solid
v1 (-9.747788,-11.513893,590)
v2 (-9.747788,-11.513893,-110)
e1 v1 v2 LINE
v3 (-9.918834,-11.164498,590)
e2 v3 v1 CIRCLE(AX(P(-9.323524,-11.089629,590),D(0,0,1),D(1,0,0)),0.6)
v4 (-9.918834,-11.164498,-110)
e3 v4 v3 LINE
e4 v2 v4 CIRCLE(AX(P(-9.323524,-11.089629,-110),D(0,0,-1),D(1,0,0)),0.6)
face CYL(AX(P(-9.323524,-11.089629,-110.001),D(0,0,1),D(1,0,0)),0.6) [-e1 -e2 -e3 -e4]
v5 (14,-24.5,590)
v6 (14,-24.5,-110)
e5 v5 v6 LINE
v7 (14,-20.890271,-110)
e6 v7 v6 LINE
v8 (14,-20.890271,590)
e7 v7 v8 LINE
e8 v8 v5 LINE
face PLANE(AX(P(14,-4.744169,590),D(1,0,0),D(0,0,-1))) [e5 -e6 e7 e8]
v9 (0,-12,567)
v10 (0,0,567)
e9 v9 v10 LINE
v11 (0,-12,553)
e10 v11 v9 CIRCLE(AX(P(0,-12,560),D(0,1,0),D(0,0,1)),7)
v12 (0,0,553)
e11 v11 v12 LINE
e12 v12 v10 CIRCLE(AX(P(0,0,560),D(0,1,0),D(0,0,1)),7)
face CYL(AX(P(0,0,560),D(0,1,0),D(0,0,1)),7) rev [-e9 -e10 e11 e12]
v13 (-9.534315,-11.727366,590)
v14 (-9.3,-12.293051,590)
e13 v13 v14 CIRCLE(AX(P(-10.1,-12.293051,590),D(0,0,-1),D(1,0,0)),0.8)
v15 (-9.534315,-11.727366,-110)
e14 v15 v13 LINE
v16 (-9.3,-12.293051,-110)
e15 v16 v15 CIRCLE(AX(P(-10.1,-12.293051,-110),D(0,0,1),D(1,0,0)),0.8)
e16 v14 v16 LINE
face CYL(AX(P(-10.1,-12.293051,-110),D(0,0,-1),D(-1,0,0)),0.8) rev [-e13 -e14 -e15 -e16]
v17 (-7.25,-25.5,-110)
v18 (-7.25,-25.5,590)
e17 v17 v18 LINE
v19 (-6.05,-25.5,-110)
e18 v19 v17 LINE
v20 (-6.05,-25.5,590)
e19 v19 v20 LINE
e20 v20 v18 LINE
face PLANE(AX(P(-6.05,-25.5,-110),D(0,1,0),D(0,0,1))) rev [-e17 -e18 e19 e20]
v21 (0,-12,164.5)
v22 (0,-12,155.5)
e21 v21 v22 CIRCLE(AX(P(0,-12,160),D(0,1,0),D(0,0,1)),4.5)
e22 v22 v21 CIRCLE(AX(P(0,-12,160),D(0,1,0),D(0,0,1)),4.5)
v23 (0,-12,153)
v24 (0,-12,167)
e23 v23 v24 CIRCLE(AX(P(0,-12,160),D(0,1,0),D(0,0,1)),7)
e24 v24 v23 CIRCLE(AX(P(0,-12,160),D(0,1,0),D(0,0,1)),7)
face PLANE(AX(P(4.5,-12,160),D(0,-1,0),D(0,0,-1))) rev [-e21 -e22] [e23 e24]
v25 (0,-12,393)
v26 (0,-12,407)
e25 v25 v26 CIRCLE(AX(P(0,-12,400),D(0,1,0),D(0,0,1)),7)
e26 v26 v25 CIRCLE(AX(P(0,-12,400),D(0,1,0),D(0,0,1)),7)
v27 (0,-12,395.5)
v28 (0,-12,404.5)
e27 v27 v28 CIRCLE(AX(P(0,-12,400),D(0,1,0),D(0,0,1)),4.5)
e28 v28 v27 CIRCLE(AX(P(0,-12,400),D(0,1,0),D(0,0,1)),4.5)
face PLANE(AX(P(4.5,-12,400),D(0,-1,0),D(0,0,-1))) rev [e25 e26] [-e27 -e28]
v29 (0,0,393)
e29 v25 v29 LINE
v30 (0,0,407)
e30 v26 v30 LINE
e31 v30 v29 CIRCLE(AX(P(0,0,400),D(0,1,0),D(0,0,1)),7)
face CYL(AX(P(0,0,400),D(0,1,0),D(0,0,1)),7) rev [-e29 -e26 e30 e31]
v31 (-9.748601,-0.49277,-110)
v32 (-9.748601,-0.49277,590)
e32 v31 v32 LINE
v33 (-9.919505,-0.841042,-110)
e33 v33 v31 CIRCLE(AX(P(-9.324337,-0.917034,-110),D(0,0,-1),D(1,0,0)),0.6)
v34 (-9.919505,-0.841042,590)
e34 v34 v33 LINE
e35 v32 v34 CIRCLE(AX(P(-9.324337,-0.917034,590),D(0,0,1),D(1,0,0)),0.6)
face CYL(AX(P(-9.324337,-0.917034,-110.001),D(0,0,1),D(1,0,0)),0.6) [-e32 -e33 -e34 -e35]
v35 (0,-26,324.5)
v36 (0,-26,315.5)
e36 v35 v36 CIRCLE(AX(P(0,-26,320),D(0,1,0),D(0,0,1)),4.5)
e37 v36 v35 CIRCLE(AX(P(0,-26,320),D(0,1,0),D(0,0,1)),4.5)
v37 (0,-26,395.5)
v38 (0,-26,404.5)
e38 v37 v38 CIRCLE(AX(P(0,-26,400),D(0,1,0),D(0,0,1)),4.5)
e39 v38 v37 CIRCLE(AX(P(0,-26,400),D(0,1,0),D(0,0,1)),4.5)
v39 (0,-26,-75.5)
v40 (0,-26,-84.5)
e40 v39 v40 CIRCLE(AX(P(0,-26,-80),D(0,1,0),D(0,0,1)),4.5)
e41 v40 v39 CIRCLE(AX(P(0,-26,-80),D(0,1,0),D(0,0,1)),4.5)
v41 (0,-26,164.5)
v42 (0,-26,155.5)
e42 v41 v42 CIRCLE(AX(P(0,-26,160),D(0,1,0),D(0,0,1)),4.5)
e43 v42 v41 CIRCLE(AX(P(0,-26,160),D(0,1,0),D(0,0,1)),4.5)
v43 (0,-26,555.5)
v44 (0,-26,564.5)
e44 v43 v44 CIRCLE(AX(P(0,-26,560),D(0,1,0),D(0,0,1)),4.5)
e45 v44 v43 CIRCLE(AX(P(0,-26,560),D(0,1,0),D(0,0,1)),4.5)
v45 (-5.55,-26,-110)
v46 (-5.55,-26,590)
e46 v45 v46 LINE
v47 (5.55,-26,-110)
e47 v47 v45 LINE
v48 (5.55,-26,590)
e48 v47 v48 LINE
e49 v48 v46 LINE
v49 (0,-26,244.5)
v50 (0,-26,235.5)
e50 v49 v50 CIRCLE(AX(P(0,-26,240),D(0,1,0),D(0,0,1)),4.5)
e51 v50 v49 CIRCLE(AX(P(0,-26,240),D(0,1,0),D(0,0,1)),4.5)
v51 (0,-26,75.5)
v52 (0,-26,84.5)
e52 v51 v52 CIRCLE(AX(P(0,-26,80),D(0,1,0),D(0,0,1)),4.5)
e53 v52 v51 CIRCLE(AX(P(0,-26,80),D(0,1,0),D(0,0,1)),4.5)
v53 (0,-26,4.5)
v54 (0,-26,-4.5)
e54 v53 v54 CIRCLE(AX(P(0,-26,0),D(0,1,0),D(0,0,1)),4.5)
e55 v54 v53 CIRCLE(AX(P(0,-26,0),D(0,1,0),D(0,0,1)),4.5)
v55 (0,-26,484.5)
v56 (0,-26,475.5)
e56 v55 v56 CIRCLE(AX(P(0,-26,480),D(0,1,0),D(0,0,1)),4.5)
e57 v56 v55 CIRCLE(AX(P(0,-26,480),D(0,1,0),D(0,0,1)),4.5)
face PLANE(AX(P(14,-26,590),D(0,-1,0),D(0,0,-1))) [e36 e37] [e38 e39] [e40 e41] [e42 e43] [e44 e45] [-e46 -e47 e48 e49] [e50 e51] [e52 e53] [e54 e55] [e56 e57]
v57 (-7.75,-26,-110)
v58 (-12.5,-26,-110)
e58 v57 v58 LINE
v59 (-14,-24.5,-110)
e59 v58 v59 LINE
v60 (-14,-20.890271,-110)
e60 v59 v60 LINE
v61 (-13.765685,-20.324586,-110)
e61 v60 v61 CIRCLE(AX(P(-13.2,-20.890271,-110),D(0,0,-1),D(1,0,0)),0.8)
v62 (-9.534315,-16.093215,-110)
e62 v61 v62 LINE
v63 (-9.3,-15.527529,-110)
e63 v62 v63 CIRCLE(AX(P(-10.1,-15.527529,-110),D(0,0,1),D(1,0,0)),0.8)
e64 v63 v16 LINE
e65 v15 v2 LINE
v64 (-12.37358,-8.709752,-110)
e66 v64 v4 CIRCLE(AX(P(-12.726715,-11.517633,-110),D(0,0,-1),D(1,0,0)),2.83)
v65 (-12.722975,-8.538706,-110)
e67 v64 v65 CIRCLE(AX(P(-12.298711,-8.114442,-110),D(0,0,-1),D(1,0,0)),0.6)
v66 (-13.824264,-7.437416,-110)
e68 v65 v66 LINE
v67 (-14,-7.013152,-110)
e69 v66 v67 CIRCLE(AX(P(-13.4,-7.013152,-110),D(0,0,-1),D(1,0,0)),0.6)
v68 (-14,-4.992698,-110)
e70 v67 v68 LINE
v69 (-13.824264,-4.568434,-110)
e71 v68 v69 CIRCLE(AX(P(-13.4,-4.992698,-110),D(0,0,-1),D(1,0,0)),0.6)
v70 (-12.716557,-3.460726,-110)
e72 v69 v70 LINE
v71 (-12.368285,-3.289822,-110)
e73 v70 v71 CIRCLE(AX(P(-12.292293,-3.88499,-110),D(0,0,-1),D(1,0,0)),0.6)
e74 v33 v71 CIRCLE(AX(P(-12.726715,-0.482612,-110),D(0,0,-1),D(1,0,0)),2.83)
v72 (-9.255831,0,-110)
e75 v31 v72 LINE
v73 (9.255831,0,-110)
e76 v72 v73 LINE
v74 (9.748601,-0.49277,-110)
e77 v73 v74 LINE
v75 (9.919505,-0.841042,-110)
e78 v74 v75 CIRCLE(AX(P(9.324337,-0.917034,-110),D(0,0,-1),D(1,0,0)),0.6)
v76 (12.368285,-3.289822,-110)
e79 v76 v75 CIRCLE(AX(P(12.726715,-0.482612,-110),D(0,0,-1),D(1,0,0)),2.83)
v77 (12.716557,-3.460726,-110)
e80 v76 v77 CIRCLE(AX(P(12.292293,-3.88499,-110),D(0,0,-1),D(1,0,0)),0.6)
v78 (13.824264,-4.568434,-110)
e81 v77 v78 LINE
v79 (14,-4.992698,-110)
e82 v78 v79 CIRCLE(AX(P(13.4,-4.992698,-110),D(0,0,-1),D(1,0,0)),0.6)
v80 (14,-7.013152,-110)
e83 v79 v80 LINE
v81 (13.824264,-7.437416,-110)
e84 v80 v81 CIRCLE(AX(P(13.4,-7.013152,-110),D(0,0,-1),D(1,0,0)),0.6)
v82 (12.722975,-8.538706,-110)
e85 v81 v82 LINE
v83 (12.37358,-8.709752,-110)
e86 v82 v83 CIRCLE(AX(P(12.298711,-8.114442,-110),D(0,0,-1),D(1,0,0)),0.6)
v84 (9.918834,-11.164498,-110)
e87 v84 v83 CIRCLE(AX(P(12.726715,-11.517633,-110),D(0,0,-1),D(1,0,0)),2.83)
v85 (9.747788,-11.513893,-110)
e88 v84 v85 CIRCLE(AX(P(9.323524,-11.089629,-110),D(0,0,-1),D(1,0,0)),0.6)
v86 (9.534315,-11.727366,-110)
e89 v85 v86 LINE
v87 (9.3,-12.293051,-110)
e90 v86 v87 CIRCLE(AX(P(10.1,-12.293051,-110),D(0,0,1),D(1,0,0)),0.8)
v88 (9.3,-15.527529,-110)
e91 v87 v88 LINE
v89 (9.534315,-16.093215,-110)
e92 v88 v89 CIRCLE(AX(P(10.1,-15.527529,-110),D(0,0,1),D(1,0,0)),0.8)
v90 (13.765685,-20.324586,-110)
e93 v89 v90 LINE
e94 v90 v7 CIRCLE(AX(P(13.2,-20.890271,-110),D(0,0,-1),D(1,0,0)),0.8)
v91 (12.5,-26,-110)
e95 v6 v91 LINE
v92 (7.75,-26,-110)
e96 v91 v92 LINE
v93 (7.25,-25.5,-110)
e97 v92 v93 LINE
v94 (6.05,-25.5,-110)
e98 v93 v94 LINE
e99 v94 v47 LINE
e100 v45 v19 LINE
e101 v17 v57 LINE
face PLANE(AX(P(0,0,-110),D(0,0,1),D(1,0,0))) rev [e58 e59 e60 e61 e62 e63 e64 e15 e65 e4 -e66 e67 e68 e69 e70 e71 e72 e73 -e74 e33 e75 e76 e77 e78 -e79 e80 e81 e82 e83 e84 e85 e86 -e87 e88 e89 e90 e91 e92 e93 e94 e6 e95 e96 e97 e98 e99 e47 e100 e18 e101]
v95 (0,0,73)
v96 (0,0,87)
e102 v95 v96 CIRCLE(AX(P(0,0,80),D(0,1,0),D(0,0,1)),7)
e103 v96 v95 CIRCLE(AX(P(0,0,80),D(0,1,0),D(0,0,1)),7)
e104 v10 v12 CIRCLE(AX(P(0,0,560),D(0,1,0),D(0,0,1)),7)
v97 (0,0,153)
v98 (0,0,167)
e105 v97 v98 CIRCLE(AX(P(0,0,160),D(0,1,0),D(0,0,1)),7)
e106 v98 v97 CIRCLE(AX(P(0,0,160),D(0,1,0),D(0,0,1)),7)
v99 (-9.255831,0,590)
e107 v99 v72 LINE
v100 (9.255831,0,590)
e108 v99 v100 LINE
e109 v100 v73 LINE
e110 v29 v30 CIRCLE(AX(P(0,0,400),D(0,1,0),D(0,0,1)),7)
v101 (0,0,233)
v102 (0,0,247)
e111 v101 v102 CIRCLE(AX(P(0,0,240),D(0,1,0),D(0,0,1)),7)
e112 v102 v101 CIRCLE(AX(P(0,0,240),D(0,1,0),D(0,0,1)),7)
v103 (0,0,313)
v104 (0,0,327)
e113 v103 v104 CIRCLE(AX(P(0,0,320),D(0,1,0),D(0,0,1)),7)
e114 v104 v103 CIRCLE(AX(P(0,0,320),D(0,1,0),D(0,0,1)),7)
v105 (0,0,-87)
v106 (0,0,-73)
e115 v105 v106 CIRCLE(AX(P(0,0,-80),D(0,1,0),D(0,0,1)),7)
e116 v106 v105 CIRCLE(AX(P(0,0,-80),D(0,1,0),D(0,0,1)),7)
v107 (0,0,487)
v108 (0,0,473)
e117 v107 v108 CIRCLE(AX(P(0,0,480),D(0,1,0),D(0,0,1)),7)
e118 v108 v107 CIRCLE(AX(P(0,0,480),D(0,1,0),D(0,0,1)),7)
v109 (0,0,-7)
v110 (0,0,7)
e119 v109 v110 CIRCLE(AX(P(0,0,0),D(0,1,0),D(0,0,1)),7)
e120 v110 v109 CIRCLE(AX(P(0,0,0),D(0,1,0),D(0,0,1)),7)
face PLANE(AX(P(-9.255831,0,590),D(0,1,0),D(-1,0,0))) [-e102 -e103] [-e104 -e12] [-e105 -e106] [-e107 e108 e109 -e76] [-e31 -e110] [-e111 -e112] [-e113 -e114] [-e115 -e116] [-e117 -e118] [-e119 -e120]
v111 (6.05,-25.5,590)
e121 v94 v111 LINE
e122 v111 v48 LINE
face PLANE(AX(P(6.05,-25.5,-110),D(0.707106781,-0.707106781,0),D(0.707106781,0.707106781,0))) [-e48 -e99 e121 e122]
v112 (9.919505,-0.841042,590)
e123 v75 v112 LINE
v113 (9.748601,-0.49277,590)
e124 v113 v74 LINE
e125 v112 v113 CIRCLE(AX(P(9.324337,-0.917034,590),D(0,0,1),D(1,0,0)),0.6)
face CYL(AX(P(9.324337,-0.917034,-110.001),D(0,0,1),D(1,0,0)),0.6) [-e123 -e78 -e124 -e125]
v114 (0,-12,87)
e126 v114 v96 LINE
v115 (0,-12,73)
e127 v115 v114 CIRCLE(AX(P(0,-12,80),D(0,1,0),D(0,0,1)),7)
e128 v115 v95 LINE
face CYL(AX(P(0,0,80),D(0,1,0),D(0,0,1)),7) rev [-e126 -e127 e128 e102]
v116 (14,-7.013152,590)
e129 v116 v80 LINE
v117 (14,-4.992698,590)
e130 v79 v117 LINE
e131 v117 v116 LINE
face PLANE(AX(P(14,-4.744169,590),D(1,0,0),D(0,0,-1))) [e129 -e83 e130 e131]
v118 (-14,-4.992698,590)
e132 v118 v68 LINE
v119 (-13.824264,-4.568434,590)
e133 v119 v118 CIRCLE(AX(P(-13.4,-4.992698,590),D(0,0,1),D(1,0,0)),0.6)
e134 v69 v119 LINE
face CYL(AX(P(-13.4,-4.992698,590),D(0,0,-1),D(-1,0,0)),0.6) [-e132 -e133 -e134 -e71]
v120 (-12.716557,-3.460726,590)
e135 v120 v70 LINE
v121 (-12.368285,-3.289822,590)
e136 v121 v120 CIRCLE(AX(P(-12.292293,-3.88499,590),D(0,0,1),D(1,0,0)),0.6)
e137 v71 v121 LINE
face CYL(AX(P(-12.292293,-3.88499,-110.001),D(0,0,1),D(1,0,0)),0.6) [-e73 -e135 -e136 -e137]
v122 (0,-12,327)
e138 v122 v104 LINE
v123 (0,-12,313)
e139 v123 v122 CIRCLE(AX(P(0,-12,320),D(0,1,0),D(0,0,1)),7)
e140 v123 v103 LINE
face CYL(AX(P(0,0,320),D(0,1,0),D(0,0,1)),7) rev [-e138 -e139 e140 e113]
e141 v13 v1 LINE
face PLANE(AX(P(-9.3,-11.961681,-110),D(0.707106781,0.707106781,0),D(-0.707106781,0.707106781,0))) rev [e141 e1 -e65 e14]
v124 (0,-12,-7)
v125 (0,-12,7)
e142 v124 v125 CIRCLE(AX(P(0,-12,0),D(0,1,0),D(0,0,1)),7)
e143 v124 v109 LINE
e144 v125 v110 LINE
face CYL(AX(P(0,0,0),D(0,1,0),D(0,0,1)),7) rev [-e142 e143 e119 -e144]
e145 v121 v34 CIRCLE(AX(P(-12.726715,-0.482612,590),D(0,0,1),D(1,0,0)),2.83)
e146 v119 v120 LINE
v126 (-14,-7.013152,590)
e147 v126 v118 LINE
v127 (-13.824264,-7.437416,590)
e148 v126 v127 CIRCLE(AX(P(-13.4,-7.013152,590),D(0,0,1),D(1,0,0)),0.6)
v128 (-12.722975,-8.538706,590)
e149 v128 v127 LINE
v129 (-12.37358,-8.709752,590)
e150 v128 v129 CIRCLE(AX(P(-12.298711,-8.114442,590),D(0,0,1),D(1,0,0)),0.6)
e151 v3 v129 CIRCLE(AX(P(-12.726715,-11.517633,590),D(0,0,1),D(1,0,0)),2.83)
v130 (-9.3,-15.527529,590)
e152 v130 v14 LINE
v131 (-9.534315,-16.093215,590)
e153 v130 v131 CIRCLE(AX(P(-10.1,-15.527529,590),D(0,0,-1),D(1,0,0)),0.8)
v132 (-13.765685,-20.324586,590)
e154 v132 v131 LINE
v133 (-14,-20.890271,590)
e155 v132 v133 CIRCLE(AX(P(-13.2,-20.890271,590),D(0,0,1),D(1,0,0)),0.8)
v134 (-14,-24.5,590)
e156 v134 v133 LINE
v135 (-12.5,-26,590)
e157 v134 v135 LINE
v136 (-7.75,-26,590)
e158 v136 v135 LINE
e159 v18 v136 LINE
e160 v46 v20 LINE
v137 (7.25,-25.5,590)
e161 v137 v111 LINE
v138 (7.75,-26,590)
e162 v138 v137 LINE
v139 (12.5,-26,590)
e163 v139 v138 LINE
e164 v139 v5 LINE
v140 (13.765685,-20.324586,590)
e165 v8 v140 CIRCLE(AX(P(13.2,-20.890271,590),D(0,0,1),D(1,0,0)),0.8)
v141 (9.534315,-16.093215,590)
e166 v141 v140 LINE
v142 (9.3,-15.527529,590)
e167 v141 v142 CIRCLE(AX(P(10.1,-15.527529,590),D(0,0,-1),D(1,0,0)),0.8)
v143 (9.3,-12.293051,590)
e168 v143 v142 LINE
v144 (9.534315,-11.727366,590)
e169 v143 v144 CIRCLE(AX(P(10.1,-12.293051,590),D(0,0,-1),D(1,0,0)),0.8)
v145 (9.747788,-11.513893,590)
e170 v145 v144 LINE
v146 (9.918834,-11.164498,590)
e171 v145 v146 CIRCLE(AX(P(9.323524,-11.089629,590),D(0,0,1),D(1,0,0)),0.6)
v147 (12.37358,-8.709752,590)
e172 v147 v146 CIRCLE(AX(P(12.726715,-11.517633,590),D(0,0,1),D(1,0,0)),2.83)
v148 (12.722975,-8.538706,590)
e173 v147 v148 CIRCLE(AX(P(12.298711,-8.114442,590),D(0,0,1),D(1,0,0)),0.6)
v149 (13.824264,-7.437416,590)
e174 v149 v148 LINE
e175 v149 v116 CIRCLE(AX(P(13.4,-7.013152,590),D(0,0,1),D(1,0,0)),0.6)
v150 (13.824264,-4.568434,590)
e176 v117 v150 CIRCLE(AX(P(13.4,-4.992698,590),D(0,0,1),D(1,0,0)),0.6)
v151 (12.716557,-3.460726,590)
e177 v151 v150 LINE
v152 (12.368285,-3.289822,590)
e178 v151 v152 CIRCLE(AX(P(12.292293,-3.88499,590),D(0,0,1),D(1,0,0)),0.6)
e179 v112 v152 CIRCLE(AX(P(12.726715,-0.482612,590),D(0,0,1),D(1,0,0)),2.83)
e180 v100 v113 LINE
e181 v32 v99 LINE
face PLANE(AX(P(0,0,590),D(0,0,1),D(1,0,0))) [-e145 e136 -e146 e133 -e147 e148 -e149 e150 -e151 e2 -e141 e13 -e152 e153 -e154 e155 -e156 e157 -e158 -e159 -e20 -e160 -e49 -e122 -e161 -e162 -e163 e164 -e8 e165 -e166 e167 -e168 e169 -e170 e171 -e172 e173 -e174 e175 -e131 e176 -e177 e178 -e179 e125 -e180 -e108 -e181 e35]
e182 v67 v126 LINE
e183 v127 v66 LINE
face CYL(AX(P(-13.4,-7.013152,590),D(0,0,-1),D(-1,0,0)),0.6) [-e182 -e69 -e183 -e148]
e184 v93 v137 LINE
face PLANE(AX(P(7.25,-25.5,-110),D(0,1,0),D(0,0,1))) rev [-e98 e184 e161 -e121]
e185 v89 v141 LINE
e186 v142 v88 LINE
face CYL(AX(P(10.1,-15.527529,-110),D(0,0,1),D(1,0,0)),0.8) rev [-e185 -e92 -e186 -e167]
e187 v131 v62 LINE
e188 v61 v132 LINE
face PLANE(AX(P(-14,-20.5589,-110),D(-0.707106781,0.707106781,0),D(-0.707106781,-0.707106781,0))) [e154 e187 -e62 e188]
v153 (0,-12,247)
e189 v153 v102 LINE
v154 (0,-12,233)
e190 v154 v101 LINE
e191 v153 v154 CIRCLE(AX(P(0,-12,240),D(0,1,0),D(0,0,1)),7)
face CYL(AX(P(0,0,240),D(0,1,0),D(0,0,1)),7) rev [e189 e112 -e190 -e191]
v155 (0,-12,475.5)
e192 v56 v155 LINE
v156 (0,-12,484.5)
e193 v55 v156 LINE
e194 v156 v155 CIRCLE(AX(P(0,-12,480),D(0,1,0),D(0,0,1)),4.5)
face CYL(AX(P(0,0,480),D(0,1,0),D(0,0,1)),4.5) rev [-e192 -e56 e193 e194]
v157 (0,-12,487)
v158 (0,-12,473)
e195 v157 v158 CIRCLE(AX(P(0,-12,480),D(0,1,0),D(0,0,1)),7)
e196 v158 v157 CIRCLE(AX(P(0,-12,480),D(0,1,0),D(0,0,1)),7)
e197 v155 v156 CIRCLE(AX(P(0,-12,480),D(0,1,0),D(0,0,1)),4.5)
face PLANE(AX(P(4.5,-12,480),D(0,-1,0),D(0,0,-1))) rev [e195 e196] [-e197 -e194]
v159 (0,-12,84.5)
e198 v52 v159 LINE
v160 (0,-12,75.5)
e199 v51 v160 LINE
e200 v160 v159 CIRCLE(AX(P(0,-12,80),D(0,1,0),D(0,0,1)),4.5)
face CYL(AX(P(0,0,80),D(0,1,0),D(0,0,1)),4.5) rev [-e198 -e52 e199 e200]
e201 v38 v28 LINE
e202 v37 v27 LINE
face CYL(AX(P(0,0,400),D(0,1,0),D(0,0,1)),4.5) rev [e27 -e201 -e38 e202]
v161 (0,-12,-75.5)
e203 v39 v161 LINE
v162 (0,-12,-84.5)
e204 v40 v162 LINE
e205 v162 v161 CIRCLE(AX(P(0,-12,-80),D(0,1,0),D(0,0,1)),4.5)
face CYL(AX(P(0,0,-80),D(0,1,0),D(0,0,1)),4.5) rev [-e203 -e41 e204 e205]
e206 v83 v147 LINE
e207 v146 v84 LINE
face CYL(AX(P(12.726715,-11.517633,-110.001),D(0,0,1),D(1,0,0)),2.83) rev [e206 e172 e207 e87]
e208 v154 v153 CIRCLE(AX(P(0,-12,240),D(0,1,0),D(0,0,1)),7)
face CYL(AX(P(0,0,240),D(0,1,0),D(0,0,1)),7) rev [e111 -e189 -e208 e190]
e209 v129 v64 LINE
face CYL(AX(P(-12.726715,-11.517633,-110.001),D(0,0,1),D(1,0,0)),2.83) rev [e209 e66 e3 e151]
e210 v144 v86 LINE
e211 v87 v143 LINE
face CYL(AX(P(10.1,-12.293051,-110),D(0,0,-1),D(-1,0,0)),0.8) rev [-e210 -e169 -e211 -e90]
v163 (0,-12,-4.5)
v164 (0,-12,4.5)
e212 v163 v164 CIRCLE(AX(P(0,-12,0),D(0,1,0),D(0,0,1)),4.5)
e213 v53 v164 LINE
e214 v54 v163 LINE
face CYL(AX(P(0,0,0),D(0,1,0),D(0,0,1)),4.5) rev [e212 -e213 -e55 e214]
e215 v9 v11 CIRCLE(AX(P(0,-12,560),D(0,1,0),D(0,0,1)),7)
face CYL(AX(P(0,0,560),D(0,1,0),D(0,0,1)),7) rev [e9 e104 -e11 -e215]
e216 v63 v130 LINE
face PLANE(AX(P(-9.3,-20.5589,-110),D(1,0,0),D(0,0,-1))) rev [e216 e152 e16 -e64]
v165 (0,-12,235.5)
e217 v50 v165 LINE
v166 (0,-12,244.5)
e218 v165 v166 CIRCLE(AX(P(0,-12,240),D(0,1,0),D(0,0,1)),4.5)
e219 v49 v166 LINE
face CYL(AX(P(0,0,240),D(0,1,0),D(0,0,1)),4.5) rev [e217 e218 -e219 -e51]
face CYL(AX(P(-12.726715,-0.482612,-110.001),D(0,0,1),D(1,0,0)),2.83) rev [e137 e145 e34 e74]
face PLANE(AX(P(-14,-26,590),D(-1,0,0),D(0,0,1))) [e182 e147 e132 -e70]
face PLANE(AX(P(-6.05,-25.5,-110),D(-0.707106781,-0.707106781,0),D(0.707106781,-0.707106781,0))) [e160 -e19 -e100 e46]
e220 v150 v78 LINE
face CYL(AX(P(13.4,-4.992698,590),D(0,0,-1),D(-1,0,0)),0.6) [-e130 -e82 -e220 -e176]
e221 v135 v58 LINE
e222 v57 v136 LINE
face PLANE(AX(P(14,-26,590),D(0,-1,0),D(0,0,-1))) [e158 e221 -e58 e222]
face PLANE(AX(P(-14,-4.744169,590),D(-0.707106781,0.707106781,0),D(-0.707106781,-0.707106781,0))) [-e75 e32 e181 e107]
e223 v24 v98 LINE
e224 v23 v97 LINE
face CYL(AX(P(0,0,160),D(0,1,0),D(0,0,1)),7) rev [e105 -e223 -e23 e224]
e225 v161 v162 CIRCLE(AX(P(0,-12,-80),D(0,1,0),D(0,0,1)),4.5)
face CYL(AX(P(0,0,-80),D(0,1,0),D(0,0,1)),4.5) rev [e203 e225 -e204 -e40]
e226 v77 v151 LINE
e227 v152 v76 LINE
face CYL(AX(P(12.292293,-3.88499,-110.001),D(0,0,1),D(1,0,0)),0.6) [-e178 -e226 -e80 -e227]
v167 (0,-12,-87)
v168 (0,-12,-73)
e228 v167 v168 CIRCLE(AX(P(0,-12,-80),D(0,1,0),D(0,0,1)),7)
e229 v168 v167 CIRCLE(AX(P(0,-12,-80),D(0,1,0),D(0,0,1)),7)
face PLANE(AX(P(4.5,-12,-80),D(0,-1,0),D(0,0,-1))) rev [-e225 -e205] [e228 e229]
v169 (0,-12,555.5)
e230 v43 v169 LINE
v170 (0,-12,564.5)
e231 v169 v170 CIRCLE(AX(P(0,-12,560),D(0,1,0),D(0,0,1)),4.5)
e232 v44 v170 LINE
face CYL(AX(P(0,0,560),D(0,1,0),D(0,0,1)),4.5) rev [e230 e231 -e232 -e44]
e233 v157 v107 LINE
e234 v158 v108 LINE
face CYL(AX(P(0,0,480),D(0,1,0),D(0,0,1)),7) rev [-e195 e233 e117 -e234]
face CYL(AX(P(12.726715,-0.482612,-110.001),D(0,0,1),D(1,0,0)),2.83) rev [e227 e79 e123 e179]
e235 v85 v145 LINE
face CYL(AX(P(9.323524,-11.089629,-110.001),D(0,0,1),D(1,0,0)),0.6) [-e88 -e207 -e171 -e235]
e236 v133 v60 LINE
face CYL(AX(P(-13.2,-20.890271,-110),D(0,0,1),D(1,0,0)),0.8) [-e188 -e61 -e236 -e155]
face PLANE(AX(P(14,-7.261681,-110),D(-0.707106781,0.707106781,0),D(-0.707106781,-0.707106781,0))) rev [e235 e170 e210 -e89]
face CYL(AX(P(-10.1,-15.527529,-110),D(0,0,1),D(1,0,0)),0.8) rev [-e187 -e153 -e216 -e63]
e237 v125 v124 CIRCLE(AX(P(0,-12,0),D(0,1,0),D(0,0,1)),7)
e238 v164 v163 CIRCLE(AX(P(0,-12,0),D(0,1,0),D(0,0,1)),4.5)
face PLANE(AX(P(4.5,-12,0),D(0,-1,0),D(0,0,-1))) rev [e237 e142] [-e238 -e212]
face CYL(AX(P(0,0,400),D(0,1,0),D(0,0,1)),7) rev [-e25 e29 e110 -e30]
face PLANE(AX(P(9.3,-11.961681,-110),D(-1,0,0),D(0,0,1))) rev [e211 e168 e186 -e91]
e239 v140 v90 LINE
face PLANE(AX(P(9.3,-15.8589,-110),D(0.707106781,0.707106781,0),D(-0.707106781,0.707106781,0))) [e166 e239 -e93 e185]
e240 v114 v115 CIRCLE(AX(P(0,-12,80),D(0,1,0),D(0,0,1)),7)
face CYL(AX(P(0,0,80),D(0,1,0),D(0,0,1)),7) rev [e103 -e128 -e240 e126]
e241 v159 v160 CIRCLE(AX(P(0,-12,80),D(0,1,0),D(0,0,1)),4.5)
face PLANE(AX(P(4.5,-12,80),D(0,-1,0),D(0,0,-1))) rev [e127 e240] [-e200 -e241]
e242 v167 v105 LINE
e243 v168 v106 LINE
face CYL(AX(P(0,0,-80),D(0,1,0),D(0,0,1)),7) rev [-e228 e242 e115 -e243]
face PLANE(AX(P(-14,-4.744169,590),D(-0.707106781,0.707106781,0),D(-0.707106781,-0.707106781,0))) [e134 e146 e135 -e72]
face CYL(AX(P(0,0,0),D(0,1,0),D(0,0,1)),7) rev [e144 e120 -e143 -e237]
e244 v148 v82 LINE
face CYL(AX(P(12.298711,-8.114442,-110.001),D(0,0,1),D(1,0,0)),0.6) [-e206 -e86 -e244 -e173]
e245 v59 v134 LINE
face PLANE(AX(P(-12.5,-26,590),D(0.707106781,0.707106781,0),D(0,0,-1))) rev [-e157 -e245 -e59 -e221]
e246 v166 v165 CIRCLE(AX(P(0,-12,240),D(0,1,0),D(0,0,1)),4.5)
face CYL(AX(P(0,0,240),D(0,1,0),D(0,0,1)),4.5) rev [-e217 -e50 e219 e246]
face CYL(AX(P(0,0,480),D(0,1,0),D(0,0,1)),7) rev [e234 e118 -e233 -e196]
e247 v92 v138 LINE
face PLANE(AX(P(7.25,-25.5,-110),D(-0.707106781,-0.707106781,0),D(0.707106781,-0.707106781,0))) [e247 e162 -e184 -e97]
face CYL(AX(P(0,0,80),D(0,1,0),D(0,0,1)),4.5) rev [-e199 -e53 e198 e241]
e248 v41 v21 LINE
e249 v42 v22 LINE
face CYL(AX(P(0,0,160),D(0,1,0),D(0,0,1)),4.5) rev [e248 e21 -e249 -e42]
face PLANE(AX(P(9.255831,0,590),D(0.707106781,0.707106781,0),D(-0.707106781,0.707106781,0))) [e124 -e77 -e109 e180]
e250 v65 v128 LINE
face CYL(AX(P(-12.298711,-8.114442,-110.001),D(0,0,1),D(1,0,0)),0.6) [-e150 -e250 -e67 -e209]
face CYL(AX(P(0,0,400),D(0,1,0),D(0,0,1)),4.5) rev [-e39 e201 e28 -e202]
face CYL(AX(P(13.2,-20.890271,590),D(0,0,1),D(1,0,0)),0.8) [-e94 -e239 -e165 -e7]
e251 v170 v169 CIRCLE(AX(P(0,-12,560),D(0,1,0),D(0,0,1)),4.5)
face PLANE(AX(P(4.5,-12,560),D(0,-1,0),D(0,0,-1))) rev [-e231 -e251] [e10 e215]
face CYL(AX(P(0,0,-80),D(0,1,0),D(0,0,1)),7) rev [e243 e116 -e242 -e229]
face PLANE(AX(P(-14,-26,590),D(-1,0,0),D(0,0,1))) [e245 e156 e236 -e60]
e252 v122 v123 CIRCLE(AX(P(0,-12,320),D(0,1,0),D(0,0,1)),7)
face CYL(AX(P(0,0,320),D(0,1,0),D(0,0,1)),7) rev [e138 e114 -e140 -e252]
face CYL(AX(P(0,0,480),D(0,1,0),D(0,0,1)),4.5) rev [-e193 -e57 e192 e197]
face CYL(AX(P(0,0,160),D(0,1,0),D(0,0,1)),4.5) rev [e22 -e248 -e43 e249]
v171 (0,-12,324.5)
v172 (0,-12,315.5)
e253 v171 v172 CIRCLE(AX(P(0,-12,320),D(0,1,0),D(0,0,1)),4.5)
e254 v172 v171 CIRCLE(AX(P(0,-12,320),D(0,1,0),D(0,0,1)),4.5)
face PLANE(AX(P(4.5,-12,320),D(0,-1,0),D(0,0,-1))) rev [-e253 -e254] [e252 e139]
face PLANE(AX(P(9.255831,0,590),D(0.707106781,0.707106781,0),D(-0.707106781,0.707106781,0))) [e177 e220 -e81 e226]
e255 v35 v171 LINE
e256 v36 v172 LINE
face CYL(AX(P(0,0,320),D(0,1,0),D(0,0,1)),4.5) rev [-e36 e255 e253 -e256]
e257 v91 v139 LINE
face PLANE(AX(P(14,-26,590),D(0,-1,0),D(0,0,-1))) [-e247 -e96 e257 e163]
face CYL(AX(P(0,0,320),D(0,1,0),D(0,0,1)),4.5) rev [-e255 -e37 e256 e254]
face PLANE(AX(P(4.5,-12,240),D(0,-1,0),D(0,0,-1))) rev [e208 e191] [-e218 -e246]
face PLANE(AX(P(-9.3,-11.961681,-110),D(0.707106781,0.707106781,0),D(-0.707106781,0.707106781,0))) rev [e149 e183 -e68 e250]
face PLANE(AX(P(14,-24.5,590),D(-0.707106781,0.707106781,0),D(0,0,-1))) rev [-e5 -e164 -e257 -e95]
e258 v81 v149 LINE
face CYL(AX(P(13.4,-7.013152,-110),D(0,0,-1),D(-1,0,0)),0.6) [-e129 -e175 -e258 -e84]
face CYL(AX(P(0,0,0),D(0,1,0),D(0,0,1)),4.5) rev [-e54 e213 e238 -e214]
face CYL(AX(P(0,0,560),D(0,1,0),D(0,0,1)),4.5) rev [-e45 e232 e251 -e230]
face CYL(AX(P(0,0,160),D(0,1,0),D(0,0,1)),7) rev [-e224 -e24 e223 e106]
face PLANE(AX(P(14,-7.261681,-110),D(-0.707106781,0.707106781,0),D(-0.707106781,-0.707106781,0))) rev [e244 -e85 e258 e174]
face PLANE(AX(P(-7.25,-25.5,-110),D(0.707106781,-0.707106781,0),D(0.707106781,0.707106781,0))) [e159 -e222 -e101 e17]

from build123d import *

# Parameters (mm, degrees)
EXTRUDE_1_DEPTH              = 700
CUT_EXTRUDE_1_DEPTH          = 701.622580281
CUT_EXTRUDE_2_REACH          = 702.623
SKETCH_4_W                   = 1.2
SKETCH_4_H                   = 0.5
CUT_EXTRUDE_3_DEPTH          = 701.622580281
SKETCH_5_W                   = 1.2
SKETCH_5_H                   = 0.5
CUT_EXTRUDE_4_DEPTH          = 701.622580281
CUT_EXTRUDE_5_DEPTH          = 701.622580281
CUT_EXTRUDE_6_REACH          = 702.623
CUT_EXTRUDE_7_REACH          = 702.623
CUT_EXTRUDE_8_REACH          = 702.623
DRAFT_1_ANGLE                = 45
DRAFT_2_ANGLE                = 45
DRAFT_3_ANGLE                = 45
DRAFT_4_ANGLE                = 45
HOLE_WIZARD_M8_1_D           = 9
HOLE_WIZARD_M8_1_CBORE_D     = 14
HOLE_WIZARD_M8_1_CBORE_DEPTH = 12
CHAMFER_1_SIZE               = 1.5
FILLET_1_R                   = 0.6
FILLET_2_R                   = 0.8


with BuildPart() as part:
    # 草图1 → 凸台-拉伸1 (new body)
    with BuildSketch(Plane(origin=(0, 0, -110), x_dir=(-1, 0, 0), z_dir=(0, 0, -1))):
        Polygon((-14, -4.744169479), (-14, -26), (14, -26), (14, -4.744169479), (9.255830521, 0), (-9.255830521, 0), align=None)
    extrude(amount=-EXTRUDE_1_DEPTH)

    # 草图2 → 切除-拉伸1 (cut, through all)
    with BuildSketch(Plane.XY.offset(590)):
        Polygon((14, -7.261680545), (9.3, -11.961680545), (9.3, -15.858900345), (14, -15.858900345), align=None)
    extrude(amount=-CUT_EXTRUDE_1_DEPTH, mode=Mode.SUBTRACT)

    # 草图3 → 切除-拉伸2 (cut, up to next)
    with BuildSketch(Plane.XY.offset(590), mode=Mode.PRIVATE) as cut_extrude_2_sk1:
        with BuildLine():
            Line((9.901074838, -11.360605707), (12.569687707, -8.691992838))
            ThreePointArc((12.569687707, -8.691992838), (10.725602827, -9.516520827), (9.901074838, -11.360605707))
        make_face()
    cut_extrude_2_tool1 = extrude(cut_extrude_2_sk1.sketch, amount=-CUT_EXTRUDE_2_REACH, mode=Mode.PRIVATE) & part.part
    add(cut_extrude_2_tool1.solids().sort_by_distance((11.029066, -9.819984, 590))[0], mode=Mode.SUBTRACT)

    # 草图4 → 切除-拉伸3 (cut, through all)
    with BuildSketch(Plane.XY.offset(590)):
        with Locations((6.65, -25.75)):
            Rectangle(SKETCH_4_W, SKETCH_4_H)
    extrude(amount=-CUT_EXTRUDE_3_DEPTH, mode=Mode.SUBTRACT)

    # 草图5 → 切除-拉伸4 (cut, through all)
    with BuildSketch(Plane.XY.offset(590)):
        with Locations((-6.65, -25.75)):
            Rectangle(SKETCH_5_W, SKETCH_5_H)
    extrude(amount=-CUT_EXTRUDE_4_DEPTH, mode=Mode.SUBTRACT)

    # 草图6 → 切除-拉伸5 (cut, through all)
    with BuildSketch(Plane.XY.offset(590)):
        Polygon((-14, -20.558900345), (-9.3, -20.558900345), (-9.3, -11.961680545), (-14, -7.261680545), align=None)
    extrude(amount=-CUT_EXTRUDE_5_DEPTH, mode=Mode.SUBTRACT)

    # 草图7 → 切除-拉伸6 (cut, up to next)
    with BuildSketch(Plane.XY.offset(590), mode=Mode.PRIVATE) as cut_extrude_6_sk1:
        with BuildLine():
            Line((-12.569687707, -8.691992838), (-9.901074838, -11.360605707))
            ThreePointArc((-9.901074838, -11.360605707), (-10.725602827, -9.516520827), (-12.569687707, -8.691992838))
        make_face()
    cut_extrude_6_tool1 = extrude(cut_extrude_6_sk1.sketch, amount=-CUT_EXTRUDE_6_REACH, mode=Mode.PRIVATE) & part.part
    add(cut_extrude_6_tool1.solids().sort_by_distance((-11.029066, -9.819984, 590))[0], mode=Mode.SUBTRACT)

    # 草图8 → 切除-拉伸7 (cut, up to next)
    with BuildSketch(Plane.XY.offset(590), mode=Mode.PRIVATE) as cut_extrude_7_sk1:
        with BuildLine():
            Line((-9.901411286, -0.645580765), (-12.563746235, -3.307915714))
            ThreePointArc((-12.563746235, -3.307915714), (-10.725602827, -2.483724173), (-9.901411286, -0.645580765))
        make_face()
    cut_extrude_7_tool1 = extrude(cut_extrude_7_sk1.sketch, amount=-CUT_EXTRUDE_7_REACH, mode=Mode.PRIVATE) & part.part
    add(cut_extrude_7_tool1.solids().sort_by_distance((-11.027412, -2.181915, 590))[0], mode=Mode.SUBTRACT)

    # 草图9 → 切除-拉伸8 (cut, up to next)
    with BuildSketch(Plane.XY.offset(590), mode=Mode.PRIVATE) as cut_extrude_8_sk1:
        with BuildLine():
            Line((12.563746235, -3.307915714), (9.901411286, -0.645580765))
            ThreePointArc((9.901411286, -0.645580765), (10.725602827, -2.483724173), (12.563746235, -3.307915714))
        make_face()
    cut_extrude_8_tool1 = extrude(cut_extrude_8_sk1.sketch, amount=-CUT_EXTRUDE_8_REACH, mode=Mode.PRIVATE) & part.part
    add(cut_extrude_8_tool1.solids().sort_by_distance((11.027412, -2.181915, 590))[0], mode=Mode.SUBTRACT)

    # 拔模1
    draft_1_faces = [part.faces().sort_by_distance(p)[0] for p in [
        (11.65, -15.858900345, 240),
    ]]
    draft(draft_1_faces, Plane(origin=(9.3, -11.961680545, -110), x_dir=(0, 0, 1), z_dir=(1, 0, 0)), DRAFT_1_ANGLE)

    # 拔模2
    draft_2_faces = [part.faces().sort_by_distance(p)[0] for p in [
        (-11.65, -20.558900345, 240),
    ]]
    draft(draft_2_faces, Plane(origin=(-14, -26, 590), x_dir=(0, 0, -1), z_dir=(-1, 0, 0)), DRAFT_2_ANGLE)

    # 拔模3
    draft_3_faces = [part.faces().sort_by_distance(p)[0] for p in [
        (6.05, -25.75, 240),
        (7.25, -25.75, 240),
    ]]
    draft(draft_3_faces, Plane(origin=(7.25, -25.5, -110), x_dir=(0, 0, -1), z_dir=(0, -1, 0)), DRAFT_3_ANGLE)

    # 拔模4
    draft_4_faces = [part.faces().sort_by_distance(p)[0] for p in [
        (-7.25, -25.75, 240),
        (-6.05, -25.75, 240),
    ]]
    draft(draft_4_faces, Plane(origin=(-6.05, -25.5, -110), x_dir=(0, 0, -1), z_dir=(0, -1, 0)), DRAFT_4_ANGLE)

    # M8 六角头螺栓的柱形沉头孔1 (through all)
    with Locations(Plane(origin=(0, 0, 0), x_dir=(1, 0, 0), z_dir=(0, 1, 0))):
        with Locations((0, -160), (0, -240), (0, -320), (0, -400), (0, -480), (0, -560), (0, 80), (0, -80), (0, 0)):
            CounterBoreHole(HOLE_WIZARD_M8_1_D / 2, HOLE_WIZARD_M8_1_CBORE_D / 2, HOLE_WIZARD_M8_1_CBORE_DEPTH)

    # 倒角1
    chamfer_1_edges = [part.edges().sort_by_distance(p)[0] for p in [
        (-14, -26, 240),
        (14, -26, 240),
    ]]
    chamfer(chamfer_1_edges, length=CHAMFER_1_SIZE)

    # 圆角1
    fillet_1_edges = [part.edges().sort_by_distance(p)[0] for p in [
        (-12.569687707, -8.691992838, 240),
        (-9.901074838, -11.360605707, 240),
        (-14, -4.744169479, 240),
        (14, -4.744169479, 240),
        (-9.901411286, -0.645580765, 240),
        (-12.563746235, -3.307915714, 240),
        (12.563746235, -3.307915714, 240),
        (9.901411286, -0.645580765, 240),
        (14, -7.261680545, 240),
        (9.901074838, -11.360605707, 240),
        (12.569687707, -8.691992838, 240),
        (-14, -7.261680545, 240),
    ]]
    fillet(fillet_1_edges, radius=FILLET_1_R)

    # 圆角2
    fillet_2_edges = [part.edges().sort_by_distance(p)[0] for p in [
        (14, -20.558900345, 240),
        (9.3, -15.858900345, 240),
        (9.3, -11.961680545, 240),
        (-14, -20.558900345, 240),
        (-9.3, -11.961680545, 240),
        (-9.3, -15.858900345, 240),
    ]]
    fillet(fillet_2_edges, radius=FILLET_2_R)


solid = part.part
